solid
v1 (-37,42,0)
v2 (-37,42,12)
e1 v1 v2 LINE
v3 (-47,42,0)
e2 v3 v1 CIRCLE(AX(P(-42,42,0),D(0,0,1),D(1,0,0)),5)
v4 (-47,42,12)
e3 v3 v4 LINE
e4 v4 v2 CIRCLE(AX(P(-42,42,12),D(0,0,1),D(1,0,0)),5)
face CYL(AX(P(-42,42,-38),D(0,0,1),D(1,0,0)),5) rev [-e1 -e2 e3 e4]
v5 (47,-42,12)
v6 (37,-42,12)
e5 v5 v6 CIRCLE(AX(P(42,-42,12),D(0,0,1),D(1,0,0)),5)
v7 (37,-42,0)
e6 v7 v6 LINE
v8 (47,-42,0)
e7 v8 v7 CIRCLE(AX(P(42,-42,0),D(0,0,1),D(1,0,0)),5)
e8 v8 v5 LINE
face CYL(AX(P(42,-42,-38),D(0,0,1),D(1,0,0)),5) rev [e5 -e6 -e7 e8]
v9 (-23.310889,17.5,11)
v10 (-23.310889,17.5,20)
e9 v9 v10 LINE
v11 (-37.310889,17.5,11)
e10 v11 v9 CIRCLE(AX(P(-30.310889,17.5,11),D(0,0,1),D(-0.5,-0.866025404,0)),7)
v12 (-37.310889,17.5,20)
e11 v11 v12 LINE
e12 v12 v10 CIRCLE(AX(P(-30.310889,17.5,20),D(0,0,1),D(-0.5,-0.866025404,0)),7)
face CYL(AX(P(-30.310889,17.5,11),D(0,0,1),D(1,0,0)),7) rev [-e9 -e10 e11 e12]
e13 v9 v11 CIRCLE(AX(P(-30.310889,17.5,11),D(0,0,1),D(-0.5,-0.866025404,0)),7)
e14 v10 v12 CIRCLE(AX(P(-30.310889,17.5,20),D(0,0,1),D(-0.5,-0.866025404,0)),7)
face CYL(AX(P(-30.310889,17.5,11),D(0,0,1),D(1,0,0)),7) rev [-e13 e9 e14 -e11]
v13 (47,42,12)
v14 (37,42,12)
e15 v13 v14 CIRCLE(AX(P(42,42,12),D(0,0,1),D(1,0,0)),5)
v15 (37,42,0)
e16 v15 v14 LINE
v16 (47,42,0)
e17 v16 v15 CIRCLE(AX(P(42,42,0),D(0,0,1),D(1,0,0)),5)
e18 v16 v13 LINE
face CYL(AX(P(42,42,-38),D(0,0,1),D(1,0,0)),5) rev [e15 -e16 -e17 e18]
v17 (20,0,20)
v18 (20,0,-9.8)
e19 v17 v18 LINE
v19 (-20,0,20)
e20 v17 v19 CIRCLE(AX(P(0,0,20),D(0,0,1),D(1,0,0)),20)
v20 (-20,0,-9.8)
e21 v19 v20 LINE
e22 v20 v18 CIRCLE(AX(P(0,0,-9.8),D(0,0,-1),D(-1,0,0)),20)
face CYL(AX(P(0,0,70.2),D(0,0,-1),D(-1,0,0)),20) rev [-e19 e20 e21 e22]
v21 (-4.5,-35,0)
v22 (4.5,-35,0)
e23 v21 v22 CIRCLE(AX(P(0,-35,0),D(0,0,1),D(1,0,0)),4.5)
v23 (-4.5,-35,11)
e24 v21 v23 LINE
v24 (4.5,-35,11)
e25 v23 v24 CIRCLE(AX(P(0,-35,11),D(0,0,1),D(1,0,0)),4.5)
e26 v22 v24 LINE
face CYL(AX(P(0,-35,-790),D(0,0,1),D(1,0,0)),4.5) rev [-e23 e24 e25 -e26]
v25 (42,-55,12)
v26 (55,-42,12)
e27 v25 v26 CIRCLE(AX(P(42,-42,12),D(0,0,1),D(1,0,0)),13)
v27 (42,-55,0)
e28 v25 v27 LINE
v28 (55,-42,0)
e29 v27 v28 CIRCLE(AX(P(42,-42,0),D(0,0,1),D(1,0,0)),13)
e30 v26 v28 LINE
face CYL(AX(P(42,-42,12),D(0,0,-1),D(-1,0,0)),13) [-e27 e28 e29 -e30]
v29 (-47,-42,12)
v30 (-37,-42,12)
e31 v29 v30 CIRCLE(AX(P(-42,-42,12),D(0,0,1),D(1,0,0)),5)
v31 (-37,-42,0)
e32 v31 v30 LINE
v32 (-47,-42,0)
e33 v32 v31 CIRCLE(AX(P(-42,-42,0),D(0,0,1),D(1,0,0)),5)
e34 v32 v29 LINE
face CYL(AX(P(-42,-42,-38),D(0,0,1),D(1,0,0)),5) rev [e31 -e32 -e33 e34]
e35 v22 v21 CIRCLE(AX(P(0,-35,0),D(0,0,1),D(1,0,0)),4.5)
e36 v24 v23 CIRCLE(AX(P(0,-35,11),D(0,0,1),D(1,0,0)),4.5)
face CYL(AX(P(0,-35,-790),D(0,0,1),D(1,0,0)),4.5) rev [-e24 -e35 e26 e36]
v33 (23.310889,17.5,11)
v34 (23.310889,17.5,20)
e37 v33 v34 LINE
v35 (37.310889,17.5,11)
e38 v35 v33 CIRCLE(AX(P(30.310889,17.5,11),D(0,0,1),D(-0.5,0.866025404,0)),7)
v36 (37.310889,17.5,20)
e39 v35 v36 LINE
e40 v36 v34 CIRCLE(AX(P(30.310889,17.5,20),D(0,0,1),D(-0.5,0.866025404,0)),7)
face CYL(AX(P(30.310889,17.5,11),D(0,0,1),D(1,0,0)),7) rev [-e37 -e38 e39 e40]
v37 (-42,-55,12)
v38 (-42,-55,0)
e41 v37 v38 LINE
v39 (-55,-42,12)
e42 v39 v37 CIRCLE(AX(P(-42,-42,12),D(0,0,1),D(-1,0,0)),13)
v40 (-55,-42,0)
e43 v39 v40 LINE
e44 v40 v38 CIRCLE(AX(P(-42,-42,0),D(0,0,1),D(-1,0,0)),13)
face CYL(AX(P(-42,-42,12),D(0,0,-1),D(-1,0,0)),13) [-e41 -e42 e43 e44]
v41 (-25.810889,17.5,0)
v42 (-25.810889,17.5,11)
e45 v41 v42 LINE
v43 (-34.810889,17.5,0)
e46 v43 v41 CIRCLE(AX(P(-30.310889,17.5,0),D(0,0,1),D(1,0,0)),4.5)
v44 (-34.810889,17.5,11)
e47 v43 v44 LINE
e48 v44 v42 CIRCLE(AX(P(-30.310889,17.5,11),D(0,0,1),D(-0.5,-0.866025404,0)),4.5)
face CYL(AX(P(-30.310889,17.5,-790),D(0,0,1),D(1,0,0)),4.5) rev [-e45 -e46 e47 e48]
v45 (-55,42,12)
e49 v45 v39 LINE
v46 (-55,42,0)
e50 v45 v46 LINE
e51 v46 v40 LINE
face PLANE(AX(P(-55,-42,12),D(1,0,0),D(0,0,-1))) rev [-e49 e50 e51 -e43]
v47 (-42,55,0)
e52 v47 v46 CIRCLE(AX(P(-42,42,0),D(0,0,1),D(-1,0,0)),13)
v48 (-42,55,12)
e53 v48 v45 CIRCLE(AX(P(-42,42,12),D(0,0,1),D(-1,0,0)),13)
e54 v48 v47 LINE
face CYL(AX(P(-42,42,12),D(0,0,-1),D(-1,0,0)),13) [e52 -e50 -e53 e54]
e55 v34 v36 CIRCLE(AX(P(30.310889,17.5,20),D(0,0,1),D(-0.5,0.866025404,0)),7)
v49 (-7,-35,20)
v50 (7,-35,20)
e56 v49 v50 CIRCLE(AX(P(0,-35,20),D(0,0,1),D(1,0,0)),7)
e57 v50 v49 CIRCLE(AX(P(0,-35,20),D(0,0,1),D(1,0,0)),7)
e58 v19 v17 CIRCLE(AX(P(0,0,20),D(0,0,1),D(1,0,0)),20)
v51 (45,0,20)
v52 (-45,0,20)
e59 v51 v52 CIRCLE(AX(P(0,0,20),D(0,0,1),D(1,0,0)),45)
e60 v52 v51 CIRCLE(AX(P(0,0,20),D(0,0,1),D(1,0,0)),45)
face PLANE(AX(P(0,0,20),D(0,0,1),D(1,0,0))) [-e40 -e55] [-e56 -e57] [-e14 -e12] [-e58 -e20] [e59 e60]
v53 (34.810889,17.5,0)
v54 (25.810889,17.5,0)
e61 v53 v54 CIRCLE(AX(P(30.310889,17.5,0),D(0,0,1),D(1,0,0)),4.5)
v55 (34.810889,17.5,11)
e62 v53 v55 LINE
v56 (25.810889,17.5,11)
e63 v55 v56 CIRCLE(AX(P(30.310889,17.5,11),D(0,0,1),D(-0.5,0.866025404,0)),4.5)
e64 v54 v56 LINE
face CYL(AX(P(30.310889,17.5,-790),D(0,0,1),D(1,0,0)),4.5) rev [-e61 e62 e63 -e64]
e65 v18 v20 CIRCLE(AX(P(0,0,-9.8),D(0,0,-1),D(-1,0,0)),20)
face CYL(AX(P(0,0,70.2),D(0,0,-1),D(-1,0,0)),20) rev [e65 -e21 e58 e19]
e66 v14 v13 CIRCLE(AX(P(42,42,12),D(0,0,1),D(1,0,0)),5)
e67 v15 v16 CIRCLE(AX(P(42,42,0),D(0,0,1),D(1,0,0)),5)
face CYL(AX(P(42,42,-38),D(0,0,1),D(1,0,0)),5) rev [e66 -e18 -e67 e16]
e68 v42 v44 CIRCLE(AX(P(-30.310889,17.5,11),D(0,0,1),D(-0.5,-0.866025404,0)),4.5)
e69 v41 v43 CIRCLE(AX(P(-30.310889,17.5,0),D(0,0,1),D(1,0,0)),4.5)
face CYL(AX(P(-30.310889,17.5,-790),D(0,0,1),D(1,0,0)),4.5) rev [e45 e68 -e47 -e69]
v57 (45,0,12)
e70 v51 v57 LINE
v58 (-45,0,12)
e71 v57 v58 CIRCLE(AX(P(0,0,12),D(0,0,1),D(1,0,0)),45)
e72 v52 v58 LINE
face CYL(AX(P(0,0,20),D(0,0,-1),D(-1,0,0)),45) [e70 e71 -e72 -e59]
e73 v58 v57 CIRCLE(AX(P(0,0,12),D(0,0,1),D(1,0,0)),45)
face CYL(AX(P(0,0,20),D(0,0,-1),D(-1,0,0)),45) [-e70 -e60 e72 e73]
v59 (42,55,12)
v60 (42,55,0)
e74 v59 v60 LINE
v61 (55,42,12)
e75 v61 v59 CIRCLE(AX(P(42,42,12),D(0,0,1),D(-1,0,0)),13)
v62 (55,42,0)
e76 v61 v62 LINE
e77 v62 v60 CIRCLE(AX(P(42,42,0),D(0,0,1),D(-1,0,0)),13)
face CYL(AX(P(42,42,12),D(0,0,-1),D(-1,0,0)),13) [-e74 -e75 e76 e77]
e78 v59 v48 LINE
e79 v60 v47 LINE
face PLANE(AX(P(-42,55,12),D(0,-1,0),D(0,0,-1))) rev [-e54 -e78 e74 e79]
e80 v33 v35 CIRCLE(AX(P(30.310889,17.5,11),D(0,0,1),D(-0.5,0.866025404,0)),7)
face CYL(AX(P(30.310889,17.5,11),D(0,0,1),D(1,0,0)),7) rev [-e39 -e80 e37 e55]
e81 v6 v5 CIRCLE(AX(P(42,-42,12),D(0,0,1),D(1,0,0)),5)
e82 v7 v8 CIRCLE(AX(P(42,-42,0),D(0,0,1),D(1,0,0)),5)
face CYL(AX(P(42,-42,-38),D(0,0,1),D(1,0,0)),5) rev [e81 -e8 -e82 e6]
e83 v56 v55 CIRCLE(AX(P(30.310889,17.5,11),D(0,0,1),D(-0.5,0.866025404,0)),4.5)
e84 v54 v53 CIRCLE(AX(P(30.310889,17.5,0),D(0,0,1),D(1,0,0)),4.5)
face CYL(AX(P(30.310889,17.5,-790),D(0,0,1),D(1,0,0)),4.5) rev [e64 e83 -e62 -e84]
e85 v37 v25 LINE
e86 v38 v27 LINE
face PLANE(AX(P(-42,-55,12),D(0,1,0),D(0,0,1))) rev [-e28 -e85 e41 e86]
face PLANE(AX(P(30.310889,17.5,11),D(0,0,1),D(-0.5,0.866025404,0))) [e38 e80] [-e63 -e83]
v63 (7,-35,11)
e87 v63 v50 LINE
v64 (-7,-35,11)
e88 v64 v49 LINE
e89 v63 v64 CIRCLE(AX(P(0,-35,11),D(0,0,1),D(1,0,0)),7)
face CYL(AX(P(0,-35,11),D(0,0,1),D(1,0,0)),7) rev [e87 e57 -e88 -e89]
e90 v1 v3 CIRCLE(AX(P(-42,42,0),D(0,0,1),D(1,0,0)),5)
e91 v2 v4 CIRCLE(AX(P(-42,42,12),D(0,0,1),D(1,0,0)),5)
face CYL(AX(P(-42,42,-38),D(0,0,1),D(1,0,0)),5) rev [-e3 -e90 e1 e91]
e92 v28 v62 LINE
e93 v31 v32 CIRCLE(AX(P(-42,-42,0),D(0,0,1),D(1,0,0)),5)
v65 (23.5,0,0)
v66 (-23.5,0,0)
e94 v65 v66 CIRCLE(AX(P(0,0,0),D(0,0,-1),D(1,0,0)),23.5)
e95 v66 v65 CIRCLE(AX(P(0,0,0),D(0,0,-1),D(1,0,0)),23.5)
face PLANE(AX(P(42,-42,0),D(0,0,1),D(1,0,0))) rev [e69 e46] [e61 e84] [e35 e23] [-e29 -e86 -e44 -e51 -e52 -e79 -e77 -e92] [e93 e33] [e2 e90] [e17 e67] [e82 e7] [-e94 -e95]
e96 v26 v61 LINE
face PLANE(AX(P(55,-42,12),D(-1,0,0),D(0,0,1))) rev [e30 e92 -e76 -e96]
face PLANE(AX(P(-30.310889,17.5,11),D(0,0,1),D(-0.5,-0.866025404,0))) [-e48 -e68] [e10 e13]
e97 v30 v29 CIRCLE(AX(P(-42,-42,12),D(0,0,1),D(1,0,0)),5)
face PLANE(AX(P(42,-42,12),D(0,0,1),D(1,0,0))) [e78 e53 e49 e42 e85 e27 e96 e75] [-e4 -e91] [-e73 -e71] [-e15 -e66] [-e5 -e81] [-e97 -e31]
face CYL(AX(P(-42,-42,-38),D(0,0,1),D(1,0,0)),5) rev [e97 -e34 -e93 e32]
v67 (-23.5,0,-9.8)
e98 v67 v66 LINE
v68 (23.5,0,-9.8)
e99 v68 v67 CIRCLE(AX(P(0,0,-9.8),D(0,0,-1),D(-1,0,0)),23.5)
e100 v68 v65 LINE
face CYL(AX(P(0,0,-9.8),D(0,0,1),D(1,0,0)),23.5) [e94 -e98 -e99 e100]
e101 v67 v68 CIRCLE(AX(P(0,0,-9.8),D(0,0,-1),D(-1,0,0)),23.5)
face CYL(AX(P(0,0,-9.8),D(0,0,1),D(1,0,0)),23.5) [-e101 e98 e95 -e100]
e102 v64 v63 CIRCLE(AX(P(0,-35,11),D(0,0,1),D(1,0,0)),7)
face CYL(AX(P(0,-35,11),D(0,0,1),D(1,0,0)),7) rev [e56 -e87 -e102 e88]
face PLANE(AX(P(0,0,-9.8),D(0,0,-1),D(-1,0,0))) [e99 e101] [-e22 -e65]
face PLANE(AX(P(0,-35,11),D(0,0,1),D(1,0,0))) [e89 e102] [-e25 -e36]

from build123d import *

# Parameters (mm, degrees)
BOSS_EXTRUDE1_DEPTH = 12
SKETCH2_R           = 5
CUT_EXTRUDE1_DEPTH  = 50
SKETCH3_R           = 45
BOSS_EXTRUDE2_DEPTH = 8
SKETCH4_R           = 23.5
BOSS_EXTRUDE3_DEPTH = 9.8
SKETCH6_R           = 20
CUT_EXTRUDE2_DEPTH  = 80
SKETCH7_R           = 7
CUT_EXTRUDE3_DEPTH  = 9
SKETCH8_R           = 4.5
CUT_EXTRUDE4_DEPTH  = 801
CIRPATTERN1_COUNT   = 3


with BuildPart() as part:
    # Sketch1 → Boss-Extrude1 (new body)
    with BuildSketch(Plane.XY):
        with BuildLine():
            Line((-42, -55), (42, -55))
            ThreePointArc((42, -55), (51.192388155, -51.192388155), (55, -42))
            Line((55, -42), (55, 42))
            ThreePointArc((55, 42), (51.192388155, 51.192388155), (42, 55))
            Line((42, 55), (-42, 55))
            ThreePointArc((-42, 55), (-51.192388155, 51.192388155), (-55, 42))
            Line((-55, 42), (-55, -42))
            ThreePointArc((-55, -42), (-51.192388155, -51.192388155), (-42, -55))
        make_face()
    extrude(amount=BOSS_EXTRUDE1_DEPTH)

    # Sketch2 → Cut-Extrude1 (cut)
    with BuildSketch(Plane.XY.offset(12)):
        with Locations((42, 42)):
            Circle(SKETCH2_R)
        with Locations((42, -42)):
            Circle(SKETCH2_R)
        with Locations((-42, -42)):
            Circle(SKETCH2_R)
        with Locations((-42, 42)):
            Circle(SKETCH2_R)
    extrude(amount=-CUT_EXTRUDE1_DEPTH, mode=Mode.SUBTRACT)

    # Sketch3 → Boss-Extrude2 (add)
    with BuildSketch(Plane.XY.offset(12)):
        Circle(SKETCH3_R)
    extrude(amount=BOSS_EXTRUDE2_DEPTH)

    # Sketch4 → Boss-Extrude3 (add)
    with BuildSketch(Plane(origin=(0, 0, 0), x_dir=(-1, 0, 0), z_dir=(0, 0, -1))):
        with Locations(Location((0, 0, 0), (0, 0, 180))):
            Circle(SKETCH4_R)
    extrude(amount=BOSS_EXTRUDE3_DEPTH)

    # Sketch6 → Cut-Extrude2 (cut)
    with BuildSketch(Plane(origin=(0, 0, -9.8), x_dir=(-1, 0, 0), z_dir=(0, 0, -1))):
        Circle(SKETCH6_R)
    extrude(amount=-CUT_EXTRUDE2_DEPTH, mode=Mode.SUBTRACT)

    # Sketch7 → Cut-Extrude3 (cut)
    with BuildSketch(Plane.XY.offset(20)):
        with Locations((0, -35)):
            Circle(SKETCH7_R)
    cut_extrude3 = extrude(amount=-CUT_EXTRUDE3_DEPTH, mode=Mode.SUBTRACT)

    # Sketch8 → Cut-Extrude4 (cut)
    with BuildSketch(Plane.XY.offset(11)):
        with Locations((0, -35)):
            Circle(SKETCH8_R)
    cut_extrude4 = extrude(amount=-CUT_EXTRUDE4_DEPTH, mode=Mode.SUBTRACT)

    # CirPattern1: Cut-Extrude3, Cut-Extrude4 ×3 about axis
    cirpattern1_axis = Axis((0, 0, 0), (0, 0, 1))
    add([cut_extrude3.rotate(cirpattern1_axis, i * 360 / CIRPATTERN1_COUNT) for i in range(1, CIRPATTERN1_COUNT)], mode=Mode.SUBTRACT)
    add([cut_extrude4.rotate(cirpattern1_axis, i * 360 / CIRPATTERN1_COUNT) for i in range(1, CIRPATTERN1_COUNT)], mode=Mode.SUBTRACT)


solid = part.part
